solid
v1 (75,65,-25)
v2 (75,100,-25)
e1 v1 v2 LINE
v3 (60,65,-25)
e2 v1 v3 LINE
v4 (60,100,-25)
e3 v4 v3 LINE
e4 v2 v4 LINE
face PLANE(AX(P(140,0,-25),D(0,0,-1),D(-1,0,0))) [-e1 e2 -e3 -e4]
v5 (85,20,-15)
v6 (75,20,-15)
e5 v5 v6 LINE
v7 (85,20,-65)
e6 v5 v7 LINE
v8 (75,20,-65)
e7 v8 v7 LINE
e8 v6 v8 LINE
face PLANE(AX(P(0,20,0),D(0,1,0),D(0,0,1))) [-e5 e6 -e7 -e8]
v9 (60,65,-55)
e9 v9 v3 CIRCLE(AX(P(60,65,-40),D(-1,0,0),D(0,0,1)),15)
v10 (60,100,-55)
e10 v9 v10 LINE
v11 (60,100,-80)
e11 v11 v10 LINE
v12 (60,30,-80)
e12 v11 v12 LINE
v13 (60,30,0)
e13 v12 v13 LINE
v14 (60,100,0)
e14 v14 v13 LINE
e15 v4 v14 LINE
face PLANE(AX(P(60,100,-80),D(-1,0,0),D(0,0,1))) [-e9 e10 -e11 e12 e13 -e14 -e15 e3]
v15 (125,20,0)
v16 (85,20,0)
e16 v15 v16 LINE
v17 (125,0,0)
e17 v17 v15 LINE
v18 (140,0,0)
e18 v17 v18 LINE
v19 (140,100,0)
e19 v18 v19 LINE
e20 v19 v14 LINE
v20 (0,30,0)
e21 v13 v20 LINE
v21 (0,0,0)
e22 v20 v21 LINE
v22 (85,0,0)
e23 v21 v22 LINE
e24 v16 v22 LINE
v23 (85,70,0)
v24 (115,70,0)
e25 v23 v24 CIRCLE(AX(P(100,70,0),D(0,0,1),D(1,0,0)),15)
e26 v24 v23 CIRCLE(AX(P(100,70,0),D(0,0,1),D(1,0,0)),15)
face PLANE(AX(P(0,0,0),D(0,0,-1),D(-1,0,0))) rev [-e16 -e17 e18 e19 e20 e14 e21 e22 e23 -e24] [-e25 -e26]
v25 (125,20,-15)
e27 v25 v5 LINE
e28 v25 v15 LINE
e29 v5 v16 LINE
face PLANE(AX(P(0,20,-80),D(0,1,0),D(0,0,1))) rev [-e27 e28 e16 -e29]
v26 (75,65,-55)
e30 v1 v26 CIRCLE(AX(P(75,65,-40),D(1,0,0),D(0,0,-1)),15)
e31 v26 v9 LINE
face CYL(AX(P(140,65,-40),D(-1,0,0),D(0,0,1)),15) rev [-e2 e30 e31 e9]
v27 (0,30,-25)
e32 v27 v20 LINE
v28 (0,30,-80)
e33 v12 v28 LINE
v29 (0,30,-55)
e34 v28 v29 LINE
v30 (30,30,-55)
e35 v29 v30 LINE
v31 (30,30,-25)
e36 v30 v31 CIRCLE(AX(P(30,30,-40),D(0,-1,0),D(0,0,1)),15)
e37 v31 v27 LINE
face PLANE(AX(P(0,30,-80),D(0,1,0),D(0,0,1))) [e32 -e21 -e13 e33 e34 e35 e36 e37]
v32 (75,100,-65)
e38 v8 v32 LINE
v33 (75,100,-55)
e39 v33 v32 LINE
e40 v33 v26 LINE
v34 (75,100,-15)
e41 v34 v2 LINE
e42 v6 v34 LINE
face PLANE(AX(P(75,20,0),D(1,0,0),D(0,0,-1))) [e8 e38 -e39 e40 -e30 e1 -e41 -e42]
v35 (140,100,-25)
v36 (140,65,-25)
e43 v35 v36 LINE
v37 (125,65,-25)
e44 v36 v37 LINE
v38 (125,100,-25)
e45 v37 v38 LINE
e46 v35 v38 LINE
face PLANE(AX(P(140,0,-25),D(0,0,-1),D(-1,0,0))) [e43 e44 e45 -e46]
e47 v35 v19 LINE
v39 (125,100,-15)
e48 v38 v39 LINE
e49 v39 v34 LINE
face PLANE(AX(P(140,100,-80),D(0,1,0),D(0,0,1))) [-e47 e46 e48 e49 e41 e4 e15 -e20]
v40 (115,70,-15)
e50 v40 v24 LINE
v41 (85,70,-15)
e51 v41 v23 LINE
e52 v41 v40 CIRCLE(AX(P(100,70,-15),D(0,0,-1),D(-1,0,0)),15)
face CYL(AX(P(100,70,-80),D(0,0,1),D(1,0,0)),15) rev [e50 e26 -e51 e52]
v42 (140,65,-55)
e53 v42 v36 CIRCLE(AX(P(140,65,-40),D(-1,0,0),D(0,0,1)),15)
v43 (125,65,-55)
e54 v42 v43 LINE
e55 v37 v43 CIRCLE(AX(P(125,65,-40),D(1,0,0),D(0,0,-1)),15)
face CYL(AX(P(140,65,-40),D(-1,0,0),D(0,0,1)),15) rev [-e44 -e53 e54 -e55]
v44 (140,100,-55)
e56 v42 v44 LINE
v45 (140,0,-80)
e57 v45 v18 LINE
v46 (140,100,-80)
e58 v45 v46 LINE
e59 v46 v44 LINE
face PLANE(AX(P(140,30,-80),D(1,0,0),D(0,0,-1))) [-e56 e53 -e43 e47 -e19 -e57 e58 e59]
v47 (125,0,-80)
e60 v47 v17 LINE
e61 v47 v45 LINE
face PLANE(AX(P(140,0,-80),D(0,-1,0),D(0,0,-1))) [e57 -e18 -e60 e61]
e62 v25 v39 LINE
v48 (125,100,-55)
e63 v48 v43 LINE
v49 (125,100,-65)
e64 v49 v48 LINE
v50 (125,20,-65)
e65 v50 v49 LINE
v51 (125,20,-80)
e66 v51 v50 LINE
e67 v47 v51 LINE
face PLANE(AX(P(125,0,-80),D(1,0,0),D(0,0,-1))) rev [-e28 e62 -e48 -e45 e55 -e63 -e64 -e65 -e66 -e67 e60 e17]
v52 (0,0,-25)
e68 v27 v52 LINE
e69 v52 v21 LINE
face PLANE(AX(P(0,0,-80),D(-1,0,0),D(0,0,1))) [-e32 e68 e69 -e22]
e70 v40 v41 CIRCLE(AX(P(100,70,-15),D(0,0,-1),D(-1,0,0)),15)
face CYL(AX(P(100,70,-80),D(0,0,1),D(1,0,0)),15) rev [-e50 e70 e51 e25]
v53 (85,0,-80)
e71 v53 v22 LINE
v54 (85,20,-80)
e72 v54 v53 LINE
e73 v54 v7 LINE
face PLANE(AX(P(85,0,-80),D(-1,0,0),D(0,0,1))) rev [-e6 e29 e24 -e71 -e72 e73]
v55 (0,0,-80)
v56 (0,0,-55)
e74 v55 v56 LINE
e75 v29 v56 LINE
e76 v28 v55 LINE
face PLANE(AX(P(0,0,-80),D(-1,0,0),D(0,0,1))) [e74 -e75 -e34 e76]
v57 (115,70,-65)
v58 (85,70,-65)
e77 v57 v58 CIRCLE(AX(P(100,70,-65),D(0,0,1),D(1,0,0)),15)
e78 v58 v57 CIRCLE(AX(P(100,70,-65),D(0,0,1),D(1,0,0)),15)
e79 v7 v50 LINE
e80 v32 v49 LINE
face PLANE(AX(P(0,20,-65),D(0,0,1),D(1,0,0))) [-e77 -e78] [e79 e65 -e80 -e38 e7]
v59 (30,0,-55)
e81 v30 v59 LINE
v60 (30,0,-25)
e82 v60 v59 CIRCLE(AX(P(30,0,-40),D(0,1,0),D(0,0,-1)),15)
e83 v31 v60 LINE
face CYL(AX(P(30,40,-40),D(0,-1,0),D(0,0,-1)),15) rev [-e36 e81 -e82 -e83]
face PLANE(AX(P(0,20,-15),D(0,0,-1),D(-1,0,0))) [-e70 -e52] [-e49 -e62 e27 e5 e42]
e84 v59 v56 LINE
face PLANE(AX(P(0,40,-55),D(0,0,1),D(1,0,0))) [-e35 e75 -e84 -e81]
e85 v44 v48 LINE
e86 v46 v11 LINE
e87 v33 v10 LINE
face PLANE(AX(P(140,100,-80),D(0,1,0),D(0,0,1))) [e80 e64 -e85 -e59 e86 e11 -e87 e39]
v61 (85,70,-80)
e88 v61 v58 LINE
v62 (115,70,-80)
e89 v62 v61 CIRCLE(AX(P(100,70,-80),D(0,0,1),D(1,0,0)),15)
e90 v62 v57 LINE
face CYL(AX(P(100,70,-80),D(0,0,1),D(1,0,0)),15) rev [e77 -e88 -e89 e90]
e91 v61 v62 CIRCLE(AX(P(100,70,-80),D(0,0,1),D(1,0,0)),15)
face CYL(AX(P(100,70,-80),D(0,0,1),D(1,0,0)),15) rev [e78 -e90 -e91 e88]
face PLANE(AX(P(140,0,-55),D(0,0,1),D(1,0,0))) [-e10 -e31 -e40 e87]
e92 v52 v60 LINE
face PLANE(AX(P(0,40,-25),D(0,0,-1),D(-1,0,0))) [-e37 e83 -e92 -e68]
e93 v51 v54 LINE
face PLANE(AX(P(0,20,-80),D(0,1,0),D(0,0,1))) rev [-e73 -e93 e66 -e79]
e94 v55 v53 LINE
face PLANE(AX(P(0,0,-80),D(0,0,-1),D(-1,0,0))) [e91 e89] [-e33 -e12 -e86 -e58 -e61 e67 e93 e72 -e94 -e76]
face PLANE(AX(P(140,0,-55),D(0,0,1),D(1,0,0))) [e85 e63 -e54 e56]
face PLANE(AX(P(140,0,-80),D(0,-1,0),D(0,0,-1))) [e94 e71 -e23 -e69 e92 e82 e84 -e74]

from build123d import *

# Parameters (mm, degrees)
BASE_BLOCK_SKETCH_W             = 140
BASE_BLOCK_SKETCH_H             = 30
BASE_BLOCK_DEPTH                = 80
BASE_NOTCH_SKETCH_W             = 40
BASE_NOTCH_SKETCH_H             = 20
BASE_NOTCH_DEPTH                = 80
UPRIGHT_SKETCH_W                = 80
UPRIGHT_SKETCH_H                = 70
UPRIGHT_DEPTH                   = 80
UPRIGHT_PROFILE_CUT_DEPTH       = 80
CROSS_HOLE_SKETCH_R             = 15
CROSS_HOLE_DEPTH                = 80
UPRIGHT_U_SLOT_DEPTH            = 80
BASE_UNDERSIDE_NOTCH_DEPTH      = 10
BASE_UNDERSIDE_NOTCH_DEPTH_BACK = 80


with BuildPart() as part:
    # Base Block Sketch → Base Block (new body)
    with BuildSketch(Plane.XY):
        with Locations((70, 15)):
            Rectangle(BASE_BLOCK_SKETCH_W, BASE_BLOCK_SKETCH_H)
    extrude(amount=-BASE_BLOCK_DEPTH)

    # Base Notch Sketch → Base Notch (cut)
    with BuildSketch(Plane.XY):
        with Locations((105, 10)):
            Rectangle(BASE_NOTCH_SKETCH_W, BASE_NOTCH_SKETCH_H)
    extrude(amount=-BASE_NOTCH_DEPTH, mode=Mode.SUBTRACT)

    # Upright Sketch → Upright (add)
    with BuildSketch(Plane.XY):
        with Locations((100, 65)):
            Rectangle(UPRIGHT_SKETCH_W, UPRIGHT_SKETCH_H)
    extrude(amount=-UPRIGHT_DEPTH)

    # Upright Profile Cut Sketch → Upright Profile Cut (cut)
    with BuildSketch(Plane(origin=(0, 100, 0), x_dir=(1, 0, 0), z_dir=(0, 1, 0))):
        Polygon((75, 15), (75, 40), (75, 65), (125, 65), (125, 15), align=None)
    extrude(amount=-UPRIGHT_PROFILE_CUT_DEPTH, mode=Mode.SUBTRACT)

    # Cross Hole Sketch → Cross Hole (cut)
    with BuildSketch(Plane.XY):
        with Locations((100, 70)):
            Circle(CROSS_HOLE_SKETCH_R)
    extrude(amount=-CROSS_HOLE_DEPTH, mode=Mode.SUBTRACT)

    # Upright U-Slot Sketch → Upright U-Slot (cut)
    with BuildSketch(Plane.ZY.offset(-60)):
        with BuildLine():
            Line((-25, 100), (-55, 100))
            Line((-55, 100), (-55, 65))
            ThreePointArc((-55, 65), (-40, 50), (-25, 65))
            Line((-25, 65), (-25, 100))
        make_face()
    extrude(amount=-UPRIGHT_U_SLOT_DEPTH, mode=Mode.SUBTRACT)

    # Base Underside Notch Sketch → Base Underside Notch (cut, two sides: drawn at the far end of the back side and taken through both)
    with BuildSketch(Plane(origin=(0, 30, 0), x_dir=(1, 0, 0), z_dir=(0, 1, 0)).offset(-BASE_UNDERSIDE_NOTCH_DEPTH_BACK)):
        with BuildLine():
            Line((30, 55), (0, 55))
            Line((0, 55), (0, 25))
            Line((0, 25), (30, 25))
            ThreePointArc((30, 25), (45, 40), (30, 55))
        make_face()
    extrude(amount=BASE_UNDERSIDE_NOTCH_DEPTH + BASE_UNDERSIDE_NOTCH_DEPTH_BACK, mode=Mode.SUBTRACT)


solid = part.part
